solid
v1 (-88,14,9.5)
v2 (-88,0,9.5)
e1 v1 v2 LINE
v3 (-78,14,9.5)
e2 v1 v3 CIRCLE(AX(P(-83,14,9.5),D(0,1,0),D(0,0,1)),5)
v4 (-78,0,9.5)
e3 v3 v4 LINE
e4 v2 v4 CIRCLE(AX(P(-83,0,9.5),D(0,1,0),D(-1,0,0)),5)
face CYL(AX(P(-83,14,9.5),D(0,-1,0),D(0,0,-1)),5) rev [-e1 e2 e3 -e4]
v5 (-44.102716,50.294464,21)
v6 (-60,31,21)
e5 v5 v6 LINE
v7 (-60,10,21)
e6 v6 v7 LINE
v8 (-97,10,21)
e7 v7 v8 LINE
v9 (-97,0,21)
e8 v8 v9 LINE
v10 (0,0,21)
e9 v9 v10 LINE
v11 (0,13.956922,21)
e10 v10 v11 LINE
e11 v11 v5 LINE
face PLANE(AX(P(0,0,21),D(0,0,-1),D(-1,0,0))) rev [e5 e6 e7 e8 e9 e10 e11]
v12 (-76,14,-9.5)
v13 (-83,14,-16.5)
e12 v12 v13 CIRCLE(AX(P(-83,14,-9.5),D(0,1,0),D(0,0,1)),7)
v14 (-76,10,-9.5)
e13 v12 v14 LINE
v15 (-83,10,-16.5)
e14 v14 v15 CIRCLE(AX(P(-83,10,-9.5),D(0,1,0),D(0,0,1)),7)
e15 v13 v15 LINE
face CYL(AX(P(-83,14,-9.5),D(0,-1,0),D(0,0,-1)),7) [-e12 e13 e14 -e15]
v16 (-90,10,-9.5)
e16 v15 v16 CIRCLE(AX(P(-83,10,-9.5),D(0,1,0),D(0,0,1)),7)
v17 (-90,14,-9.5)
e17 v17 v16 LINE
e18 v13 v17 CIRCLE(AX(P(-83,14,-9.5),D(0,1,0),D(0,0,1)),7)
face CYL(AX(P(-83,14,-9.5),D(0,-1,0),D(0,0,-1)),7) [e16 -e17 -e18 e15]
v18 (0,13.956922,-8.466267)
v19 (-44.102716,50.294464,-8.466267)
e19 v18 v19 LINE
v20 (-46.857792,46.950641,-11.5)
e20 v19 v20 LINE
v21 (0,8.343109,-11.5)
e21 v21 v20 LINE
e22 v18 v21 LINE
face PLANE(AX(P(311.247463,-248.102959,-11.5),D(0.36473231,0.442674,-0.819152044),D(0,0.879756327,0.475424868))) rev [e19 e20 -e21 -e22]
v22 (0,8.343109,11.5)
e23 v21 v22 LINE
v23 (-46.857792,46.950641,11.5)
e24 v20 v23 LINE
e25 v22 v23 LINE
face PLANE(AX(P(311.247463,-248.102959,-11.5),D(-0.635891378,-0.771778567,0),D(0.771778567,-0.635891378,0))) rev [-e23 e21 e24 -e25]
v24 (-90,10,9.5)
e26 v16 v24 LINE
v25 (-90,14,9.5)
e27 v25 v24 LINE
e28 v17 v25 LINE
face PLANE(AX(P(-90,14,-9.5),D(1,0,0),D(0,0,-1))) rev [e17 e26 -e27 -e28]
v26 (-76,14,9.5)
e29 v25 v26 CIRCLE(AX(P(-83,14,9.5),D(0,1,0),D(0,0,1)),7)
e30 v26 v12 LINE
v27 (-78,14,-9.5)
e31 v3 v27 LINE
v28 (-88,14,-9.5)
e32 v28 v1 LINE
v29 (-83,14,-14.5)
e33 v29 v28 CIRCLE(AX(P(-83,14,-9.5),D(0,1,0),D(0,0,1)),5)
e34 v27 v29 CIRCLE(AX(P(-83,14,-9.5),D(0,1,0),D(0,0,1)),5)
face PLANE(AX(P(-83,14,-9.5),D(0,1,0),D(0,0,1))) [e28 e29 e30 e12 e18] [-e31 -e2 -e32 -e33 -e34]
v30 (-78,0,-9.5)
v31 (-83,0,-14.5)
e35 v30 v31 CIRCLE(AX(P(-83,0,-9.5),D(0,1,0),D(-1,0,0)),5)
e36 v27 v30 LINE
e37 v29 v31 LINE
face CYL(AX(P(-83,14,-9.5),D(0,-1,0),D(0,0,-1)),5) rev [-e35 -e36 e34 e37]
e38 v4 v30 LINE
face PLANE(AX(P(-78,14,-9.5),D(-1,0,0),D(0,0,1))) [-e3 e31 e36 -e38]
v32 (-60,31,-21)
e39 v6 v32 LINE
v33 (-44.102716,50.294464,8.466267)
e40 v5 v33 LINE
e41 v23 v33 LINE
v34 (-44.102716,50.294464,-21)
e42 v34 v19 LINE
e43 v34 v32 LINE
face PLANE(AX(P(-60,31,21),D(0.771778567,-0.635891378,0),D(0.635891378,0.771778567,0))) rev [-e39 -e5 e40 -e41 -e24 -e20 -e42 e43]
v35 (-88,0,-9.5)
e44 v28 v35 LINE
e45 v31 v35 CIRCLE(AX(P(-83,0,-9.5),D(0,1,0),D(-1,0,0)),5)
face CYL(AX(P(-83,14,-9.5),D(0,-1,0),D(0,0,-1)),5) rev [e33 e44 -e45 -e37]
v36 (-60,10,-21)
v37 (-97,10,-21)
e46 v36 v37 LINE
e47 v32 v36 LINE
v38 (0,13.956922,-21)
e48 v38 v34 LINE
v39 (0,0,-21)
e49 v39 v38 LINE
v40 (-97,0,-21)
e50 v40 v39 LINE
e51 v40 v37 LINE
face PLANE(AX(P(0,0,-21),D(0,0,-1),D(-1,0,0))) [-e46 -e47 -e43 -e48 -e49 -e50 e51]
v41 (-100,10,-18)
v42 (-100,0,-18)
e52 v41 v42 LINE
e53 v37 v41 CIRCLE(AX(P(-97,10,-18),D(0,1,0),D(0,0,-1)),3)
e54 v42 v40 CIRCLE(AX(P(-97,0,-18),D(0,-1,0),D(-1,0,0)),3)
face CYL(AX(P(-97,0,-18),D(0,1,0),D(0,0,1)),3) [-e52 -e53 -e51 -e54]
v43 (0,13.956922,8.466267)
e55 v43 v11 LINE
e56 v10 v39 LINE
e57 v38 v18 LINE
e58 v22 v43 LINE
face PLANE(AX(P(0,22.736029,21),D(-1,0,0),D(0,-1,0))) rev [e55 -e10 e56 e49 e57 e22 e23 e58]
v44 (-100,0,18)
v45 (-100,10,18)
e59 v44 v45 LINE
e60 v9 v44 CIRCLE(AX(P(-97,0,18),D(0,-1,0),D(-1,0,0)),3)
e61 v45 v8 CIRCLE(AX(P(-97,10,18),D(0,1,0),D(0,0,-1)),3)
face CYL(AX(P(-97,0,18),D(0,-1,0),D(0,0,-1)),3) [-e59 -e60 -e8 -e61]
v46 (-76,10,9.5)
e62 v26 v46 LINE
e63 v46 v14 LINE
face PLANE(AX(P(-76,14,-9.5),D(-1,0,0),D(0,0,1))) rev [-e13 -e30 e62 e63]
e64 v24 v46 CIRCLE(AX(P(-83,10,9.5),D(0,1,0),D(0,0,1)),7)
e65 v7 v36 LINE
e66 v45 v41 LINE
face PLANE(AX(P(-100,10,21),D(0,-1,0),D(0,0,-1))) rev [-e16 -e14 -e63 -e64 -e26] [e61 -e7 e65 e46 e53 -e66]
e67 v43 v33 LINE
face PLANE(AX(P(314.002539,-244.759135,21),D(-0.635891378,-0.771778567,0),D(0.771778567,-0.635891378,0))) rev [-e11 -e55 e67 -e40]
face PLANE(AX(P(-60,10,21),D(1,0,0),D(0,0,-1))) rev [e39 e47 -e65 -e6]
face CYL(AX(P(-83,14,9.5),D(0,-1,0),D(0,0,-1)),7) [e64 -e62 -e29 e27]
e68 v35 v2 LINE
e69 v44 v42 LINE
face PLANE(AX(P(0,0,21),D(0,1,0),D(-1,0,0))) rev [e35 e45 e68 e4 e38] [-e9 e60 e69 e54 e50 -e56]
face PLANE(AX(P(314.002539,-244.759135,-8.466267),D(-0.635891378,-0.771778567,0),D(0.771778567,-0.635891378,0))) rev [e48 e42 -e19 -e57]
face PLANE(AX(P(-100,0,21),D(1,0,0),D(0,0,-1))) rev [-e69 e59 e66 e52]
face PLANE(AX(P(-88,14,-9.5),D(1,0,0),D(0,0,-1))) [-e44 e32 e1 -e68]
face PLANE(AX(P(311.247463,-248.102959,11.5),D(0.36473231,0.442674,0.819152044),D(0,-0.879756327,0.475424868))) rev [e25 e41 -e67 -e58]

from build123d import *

# Parameters (mm, degrees)
BASE_BLOCK_DEPTH         = 21
SLOT_BOSS_DEPTH          = 4
MOUNTING_START           = -34
MOUNTING_SLOT_DEPTH      = 34
DOVETAIL_GROOVE_55_DEPTH = 464
EDGE_FILLET_R3_R         = 3


with BuildPart() as part:
    # Base Profile Sketch → Base Block (new, symmetric)
    with BuildSketch(Plane.XY):
        Polygon((0, 0), (-100, 0), (-100, 10), (-60, 10), (-60, 31), (-44.102715558, 50.294464164), (0, 22.736028876), align=None)
    extrude(amount=BASE_BLOCK_DEPTH, both=True)

    # Slot Boss Sketch → Slot Boss (add)
    with BuildSketch(Plane(origin=(0, 10, 0), x_dir=(1, 0, 0), z_dir=(0, 1, 0))):
        with BuildLine():
            Line((-90, 9.5), (-90, -9.5))
            ThreePointArc((-90, -9.5), (-83, -16.5), (-76, -9.5))
            Line((-76, -9.5), (-76, 9.5))
            ThreePointArc((-76, 9.5), (-83, 16.5), (-90, 9.5))
        make_face()
        with BuildLine():
            Line((-88, 9.5), (-88, -9.5))
            ThreePointArc((-88, -9.5), (-83, -14.5), (-78, -9.5))
            Line((-78, -9.5), (-78, 9.5))
            ThreePointArc((-78, 9.5), (-83, 14.5), (-88, 9.5))
        make_face(mode=Mode.SUBTRACT)
    extrude(amount=SLOT_BOSS_DEPTH)

    # Mounting Slot Sketch → Mounting Slot (cut)
    with BuildSketch(Plane(origin=(0, 10, 0), x_dir=(1, 0, 0), z_dir=(0, 1, 0)).offset(MOUNTING_START)):
        with BuildLine():
            Line((-88, 9.5), (-88, -9.5))
            ThreePointArc((-88, -9.5), (-83, -14.5), (-78, -9.5))
            Line((-78, -9.5), (-78, 9.5))
            ThreePointArc((-78, 9.5), (-83, 14.5), (-88, 9.5))
        make_face()
    extrude(amount=MOUNTING_SLOT_DEPTH, mode=Mode.SUBTRACT)

    # Dovetail Groove Sketch → Dovetail Groove 55° (cut)
    with BuildSketch(Plane(origin=(-50.952316762, 41.981133327, 0), x_dir=(0, 0, 1), z_dir=(-0.7717785665555229, 0.635891377678218, 0))):
        Polygon((-11.5, 6.439032464), (-8.466266509, 10.771652903), (-21, 10.771652903), (-21, 17.547179775), (21, 17.547179775), (21, 10.771652903), (8.466266509, 10.771652903), (11.5, 6.439032464), align=None)
    extrude(amount=-DOVETAIL_GROOVE_55_DEPTH, mode=Mode.SUBTRACT)

    # Edge Fillet R3
    edge_fillet_r3_edges = [part.edges().sort_by_distance(p)[0] for p in [
        (-100, 5, 21),
        (-100, 5, -21),
    ]]
    fillet(edge_fillet_r3_edges, radius=EDGE_FILLET_R3_R)


solid = part.part
